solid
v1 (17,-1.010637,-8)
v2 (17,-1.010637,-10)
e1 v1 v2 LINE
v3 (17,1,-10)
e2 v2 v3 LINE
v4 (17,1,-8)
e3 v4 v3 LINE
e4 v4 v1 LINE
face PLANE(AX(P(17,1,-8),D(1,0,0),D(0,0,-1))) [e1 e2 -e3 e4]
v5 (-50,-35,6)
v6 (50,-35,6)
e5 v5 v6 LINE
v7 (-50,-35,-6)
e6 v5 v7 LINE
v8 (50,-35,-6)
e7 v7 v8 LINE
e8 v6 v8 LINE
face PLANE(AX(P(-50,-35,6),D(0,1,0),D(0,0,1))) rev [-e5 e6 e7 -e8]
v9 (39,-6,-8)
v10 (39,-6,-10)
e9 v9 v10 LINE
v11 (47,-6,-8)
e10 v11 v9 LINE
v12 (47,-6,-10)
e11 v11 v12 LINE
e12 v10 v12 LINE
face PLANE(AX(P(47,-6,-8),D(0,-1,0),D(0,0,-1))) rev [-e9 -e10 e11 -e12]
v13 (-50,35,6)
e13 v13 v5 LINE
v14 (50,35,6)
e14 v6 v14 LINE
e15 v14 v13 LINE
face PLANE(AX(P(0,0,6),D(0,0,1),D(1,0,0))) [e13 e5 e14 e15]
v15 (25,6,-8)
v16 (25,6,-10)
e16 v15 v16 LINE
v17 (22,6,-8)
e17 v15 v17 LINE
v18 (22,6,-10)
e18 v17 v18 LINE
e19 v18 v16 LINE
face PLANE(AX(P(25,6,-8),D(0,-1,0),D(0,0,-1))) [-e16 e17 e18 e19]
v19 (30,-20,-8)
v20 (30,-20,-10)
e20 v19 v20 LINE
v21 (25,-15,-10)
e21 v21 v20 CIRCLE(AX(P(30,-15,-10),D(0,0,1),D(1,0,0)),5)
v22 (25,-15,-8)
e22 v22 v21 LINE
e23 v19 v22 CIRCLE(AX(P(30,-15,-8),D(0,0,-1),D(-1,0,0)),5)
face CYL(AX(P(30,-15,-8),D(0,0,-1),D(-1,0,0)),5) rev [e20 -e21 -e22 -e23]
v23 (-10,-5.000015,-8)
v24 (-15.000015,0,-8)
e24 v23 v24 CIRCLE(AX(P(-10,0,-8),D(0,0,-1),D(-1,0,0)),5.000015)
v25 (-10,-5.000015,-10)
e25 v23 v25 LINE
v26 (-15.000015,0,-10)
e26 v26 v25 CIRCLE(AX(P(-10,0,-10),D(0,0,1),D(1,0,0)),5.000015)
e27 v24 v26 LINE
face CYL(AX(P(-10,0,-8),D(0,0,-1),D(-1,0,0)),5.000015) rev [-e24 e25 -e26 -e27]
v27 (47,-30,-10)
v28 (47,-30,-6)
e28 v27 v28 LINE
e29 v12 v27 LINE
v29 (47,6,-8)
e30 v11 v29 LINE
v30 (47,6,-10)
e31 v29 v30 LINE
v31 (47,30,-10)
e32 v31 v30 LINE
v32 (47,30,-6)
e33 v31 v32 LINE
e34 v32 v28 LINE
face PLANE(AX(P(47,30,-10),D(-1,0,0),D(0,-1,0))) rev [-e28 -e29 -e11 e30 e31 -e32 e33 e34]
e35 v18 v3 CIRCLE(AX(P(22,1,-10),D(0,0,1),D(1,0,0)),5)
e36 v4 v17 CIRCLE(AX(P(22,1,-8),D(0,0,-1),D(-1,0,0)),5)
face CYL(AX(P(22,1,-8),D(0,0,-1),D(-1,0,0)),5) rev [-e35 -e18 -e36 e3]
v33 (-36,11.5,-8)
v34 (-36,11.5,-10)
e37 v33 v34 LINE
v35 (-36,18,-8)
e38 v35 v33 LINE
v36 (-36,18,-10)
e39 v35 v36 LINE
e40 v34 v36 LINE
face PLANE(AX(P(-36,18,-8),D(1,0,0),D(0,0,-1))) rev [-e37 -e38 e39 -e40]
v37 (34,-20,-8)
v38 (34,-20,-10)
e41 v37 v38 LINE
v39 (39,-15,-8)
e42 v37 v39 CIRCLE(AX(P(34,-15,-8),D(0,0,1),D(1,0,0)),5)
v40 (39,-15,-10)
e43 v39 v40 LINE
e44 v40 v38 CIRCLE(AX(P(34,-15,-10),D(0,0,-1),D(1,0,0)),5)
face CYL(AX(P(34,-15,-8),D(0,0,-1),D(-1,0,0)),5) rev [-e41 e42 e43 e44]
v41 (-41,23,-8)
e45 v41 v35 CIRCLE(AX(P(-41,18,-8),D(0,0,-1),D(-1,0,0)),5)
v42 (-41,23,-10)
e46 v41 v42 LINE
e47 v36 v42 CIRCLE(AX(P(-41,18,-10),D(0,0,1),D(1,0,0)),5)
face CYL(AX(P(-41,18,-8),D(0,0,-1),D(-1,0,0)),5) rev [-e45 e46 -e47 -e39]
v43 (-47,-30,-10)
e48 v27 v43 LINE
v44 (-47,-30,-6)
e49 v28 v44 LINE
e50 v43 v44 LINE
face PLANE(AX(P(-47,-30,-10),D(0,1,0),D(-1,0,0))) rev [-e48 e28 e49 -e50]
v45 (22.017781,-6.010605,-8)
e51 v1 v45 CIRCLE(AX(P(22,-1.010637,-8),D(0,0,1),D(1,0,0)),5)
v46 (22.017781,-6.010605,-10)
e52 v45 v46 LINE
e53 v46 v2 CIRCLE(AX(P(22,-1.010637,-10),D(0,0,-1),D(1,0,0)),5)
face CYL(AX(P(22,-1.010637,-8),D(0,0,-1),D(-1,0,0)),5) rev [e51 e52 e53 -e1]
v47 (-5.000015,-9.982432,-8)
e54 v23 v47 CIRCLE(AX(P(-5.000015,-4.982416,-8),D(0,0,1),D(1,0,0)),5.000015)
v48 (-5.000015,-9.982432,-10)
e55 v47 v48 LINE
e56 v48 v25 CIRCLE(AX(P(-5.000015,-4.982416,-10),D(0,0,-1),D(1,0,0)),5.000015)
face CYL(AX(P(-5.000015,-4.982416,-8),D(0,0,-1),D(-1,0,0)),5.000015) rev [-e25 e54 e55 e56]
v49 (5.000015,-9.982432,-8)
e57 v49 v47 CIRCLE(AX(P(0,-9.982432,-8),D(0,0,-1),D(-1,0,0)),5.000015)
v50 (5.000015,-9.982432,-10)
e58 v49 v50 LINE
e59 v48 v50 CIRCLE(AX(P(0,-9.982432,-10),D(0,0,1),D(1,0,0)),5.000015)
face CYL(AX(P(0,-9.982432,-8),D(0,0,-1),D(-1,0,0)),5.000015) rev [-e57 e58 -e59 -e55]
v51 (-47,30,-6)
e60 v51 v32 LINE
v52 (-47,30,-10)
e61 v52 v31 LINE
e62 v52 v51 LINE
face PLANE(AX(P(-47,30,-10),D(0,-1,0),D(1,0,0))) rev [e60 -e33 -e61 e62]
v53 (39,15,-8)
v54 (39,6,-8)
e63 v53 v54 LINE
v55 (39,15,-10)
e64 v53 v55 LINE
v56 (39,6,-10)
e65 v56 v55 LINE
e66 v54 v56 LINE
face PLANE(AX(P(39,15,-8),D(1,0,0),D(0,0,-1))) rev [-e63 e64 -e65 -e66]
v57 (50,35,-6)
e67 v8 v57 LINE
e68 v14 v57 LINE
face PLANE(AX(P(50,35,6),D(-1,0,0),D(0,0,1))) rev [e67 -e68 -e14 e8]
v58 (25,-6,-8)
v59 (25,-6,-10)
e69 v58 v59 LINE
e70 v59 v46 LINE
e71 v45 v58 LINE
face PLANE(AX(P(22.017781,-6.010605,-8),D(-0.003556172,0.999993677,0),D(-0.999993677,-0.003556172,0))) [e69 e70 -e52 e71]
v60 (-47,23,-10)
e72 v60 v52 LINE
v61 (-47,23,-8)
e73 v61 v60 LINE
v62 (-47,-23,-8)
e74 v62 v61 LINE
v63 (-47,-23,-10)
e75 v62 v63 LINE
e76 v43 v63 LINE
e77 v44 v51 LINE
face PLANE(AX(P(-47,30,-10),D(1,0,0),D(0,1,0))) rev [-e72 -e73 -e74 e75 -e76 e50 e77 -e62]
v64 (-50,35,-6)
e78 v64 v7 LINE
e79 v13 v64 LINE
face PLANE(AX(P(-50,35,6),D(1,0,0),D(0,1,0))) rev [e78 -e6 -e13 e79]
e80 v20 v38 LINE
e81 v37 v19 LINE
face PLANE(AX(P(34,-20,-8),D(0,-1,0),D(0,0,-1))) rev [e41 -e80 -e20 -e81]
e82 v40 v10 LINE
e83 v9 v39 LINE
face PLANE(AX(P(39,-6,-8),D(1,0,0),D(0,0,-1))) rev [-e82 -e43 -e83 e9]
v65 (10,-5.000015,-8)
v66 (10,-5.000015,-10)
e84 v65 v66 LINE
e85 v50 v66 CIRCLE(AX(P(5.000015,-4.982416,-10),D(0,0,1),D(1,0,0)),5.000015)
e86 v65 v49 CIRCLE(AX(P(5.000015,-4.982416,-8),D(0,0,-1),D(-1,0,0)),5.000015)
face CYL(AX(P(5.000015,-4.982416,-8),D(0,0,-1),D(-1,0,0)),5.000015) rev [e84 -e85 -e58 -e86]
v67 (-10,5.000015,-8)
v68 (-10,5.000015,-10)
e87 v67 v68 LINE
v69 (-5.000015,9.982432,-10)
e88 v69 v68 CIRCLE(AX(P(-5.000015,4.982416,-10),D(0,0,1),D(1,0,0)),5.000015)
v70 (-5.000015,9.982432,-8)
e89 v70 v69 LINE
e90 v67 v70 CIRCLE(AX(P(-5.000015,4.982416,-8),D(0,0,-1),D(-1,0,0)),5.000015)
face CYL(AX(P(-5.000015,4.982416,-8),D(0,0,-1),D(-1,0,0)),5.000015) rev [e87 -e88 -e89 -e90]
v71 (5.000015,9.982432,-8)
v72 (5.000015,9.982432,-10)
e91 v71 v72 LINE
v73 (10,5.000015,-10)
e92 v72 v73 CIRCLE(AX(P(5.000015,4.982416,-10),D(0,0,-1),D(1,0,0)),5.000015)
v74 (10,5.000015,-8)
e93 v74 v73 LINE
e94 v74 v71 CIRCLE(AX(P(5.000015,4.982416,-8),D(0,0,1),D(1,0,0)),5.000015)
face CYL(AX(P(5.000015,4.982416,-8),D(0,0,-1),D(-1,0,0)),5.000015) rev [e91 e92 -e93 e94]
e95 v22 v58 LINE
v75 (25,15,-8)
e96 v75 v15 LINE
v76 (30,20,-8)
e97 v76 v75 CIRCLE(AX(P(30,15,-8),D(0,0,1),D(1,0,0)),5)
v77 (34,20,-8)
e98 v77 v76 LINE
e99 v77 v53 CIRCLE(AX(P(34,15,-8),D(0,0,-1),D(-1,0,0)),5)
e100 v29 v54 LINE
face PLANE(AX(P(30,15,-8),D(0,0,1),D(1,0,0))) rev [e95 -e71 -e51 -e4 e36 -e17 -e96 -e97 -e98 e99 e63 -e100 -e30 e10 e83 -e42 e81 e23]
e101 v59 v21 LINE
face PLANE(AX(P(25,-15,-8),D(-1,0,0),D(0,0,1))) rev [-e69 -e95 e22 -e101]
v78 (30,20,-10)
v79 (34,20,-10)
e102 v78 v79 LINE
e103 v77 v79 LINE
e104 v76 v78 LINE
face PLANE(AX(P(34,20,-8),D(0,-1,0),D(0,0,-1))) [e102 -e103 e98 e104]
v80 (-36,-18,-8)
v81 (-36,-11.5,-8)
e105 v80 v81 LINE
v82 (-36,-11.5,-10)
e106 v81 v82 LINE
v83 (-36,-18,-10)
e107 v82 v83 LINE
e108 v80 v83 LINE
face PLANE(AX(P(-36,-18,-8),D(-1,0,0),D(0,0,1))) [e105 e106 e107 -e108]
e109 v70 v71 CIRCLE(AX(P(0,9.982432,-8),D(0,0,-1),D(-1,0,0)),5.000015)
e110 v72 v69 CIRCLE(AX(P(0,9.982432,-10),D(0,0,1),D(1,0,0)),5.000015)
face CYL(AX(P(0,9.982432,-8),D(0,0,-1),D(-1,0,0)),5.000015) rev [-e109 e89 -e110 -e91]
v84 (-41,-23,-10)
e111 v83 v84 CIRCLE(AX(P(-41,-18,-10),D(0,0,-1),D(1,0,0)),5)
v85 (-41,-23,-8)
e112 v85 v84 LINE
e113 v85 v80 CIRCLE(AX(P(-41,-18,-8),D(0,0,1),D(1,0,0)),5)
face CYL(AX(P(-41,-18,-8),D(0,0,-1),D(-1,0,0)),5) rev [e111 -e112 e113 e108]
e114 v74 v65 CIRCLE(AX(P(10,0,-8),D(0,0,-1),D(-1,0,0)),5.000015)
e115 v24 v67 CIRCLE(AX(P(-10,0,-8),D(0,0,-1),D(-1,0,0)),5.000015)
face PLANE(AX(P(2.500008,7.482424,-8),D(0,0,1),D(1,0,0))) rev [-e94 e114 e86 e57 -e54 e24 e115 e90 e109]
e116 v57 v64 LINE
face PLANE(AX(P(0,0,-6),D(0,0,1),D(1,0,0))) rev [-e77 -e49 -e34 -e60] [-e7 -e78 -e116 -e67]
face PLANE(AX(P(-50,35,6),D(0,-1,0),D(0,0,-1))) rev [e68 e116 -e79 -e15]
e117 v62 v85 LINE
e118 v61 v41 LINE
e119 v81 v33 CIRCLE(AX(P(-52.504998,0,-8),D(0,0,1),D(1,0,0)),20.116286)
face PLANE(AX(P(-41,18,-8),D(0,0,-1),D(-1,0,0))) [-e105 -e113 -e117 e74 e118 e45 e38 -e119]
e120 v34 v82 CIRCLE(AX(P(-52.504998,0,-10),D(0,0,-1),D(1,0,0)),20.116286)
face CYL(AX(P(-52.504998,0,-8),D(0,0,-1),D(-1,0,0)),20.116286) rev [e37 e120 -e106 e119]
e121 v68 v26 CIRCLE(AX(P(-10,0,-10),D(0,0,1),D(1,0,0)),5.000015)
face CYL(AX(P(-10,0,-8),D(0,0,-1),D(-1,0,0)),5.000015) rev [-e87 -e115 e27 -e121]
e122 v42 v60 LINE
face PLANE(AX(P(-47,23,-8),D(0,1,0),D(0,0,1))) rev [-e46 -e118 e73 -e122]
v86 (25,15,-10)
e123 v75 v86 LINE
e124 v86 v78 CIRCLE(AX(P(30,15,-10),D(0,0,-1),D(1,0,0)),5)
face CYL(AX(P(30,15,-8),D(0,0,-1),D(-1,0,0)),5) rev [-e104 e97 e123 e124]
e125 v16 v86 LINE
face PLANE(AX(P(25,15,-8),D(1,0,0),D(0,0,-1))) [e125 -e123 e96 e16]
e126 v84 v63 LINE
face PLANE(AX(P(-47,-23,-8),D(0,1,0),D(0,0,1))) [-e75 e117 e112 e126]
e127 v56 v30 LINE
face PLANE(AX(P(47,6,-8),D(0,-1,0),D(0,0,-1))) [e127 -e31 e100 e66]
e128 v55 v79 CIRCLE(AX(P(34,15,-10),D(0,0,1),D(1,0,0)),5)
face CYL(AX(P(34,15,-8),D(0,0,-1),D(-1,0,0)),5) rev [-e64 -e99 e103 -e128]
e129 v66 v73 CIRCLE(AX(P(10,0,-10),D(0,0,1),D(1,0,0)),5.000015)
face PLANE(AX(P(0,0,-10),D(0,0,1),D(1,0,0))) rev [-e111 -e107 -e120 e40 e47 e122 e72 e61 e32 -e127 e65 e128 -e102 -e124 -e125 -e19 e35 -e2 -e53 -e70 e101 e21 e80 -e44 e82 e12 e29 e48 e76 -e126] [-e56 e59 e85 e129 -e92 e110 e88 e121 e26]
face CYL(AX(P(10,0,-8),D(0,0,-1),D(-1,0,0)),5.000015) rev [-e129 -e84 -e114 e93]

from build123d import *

# Parameters (mm, degrees)
BASE_PLATE_SKETCH_W        = 100
BASE_PLATE_SKETCH_H        = 70
BASE_PLATE_100X70X12_DEPTH = 6
RAISED_PAD_SKETCH_W        = 94
RAISED_PAD_SKETCH_H        = 60
RAISED_PAD_94X60X4_DEPTH   = 4
PAD_CUT_1_DEPTH            = 2
PAD_CUT_2_DEPTH            = 2
PAD_CUT_3_DEPTH            = 2


with BuildPart() as part:
    # Base Plate Sketch → Base Plate 100x70x12 (new, symmetric)
    with BuildSketch(Plane.XY):
        Rectangle(BASE_PLATE_SKETCH_W, BASE_PLATE_SKETCH_H)
    extrude(amount=BASE_PLATE_100X70X12_DEPTH, both=True)

    # Raised Pad Sketch → Raised Pad 94x60x4 (add)
    with BuildSketch(Plane(origin=(0, 0, -6), x_dir=(-1, 0, 0), z_dir=(0, 0, -1))):
        Rectangle(RAISED_PAD_SKETCH_W, RAISED_PAD_SKETCH_H)
    extrude(amount=RAISED_PAD_94X60X4_DEPTH)

    # Pad Cut 1 Sketch → Pad Cut 1 (cut, symmetric)
    with BuildSketch(Plane(origin=(0, 0, -10), x_dir=(-1, 0, 0), z_dir=(0, 0, -1))):
        with BuildLine():
            Line((47, -23), (47, 23))
            Line((47, 23), (41, 23))
            ThreePointArc((41, 23), (37.464466094, 21.535533906), (36, 18))
            Line((36, 18), (36, 11.5))
            ThreePointArc((36, 11.5), (32.388712156, 0), (36, -11.5))
            Line((36, -11.5), (36, -18))
            ThreePointArc((36, -18), (37.464466094, -21.535533906), (41, -23))
            Line((41, -23), (47, -23))
        make_face()
    extrude(amount=PAD_CUT_1_DEPTH, both=True, mode=Mode.SUBTRACT)

    # Pad Cut 2 Sketch → Pad Cut 2 (cut, symmetric)
    with BuildSketch(Plane(origin=(0, 0, -10), x_dir=(-1, 0, 0), z_dir=(0, 0, -1))):
        with BuildLine():
            Line((-47, -6), (-39, -6))
            Line((-39, -6), (-39, -15))
            ThreePointArc((-39, -15), (-37.535533906, -18.535533906), (-34, -20))
            Line((-34, -20), (-30, -20))
            ThreePointArc((-30, -20), (-26.464466094, -18.535533906), (-25, -15))
            Line((-25, -15), (-25, -6))
            Line((-25, -6), (-22.017780858, -6.01060535))
            ThreePointArc((-22.017780858, -6.01060535), (-18.470758176, -4.552451776), (-17, -1.010636966))
            Line((-17, -1.010636966), (-17, 1))
            ThreePointArc((-17, 1), (-18.464466094, 4.535533906), (-22, 6))
            Line((-22, 6), (-25, 6))
            Line((-25, 6), (-25, 15))
            ThreePointArc((-25, 15), (-26.464466094, 18.535533906), (-30, 20))
            Line((-30, 20), (-34, 20))
            ThreePointArc((-34, 20), (-37.535533906, 18.535533906), (-39, 15))
            Line((-39, 15), (-39, 6))
            Line((-39, 6), (-47, 6))
            Line((-47, 6), (-47, -6))
        make_face()
    extrude(amount=PAD_CUT_2_DEPTH, both=True, mode=Mode.SUBTRACT)

    # Pad Cut 3 Sketch → Pad Cut 3 (cut, symmetric)
    with BuildSketch(Plane(origin=(0, 0, -10), x_dir=(-1, 0, 0), z_dir=(0, 0, -1))):
        with BuildLine():
            ThreePointArc((-10, 5.000015487), (-15.000015487, 0), (-10, -5.000015487))
            ThreePointArc((-10, -5.000015487), (-8.529332614, -8.524177957), (-5.000015487, -9.982431809))
            ThreePointArc((-5.000015487, -9.982431809), (0, -14.982447295), (5.000015487, -9.982431809))
            ThreePointArc((5.000015487, -9.982431809), (8.529332614, -8.524177957), (10, -5.000015487))
            ThreePointArc((10, -5.000015487), (15.000015487, 0), (10, 5.000015487))
            ThreePointArc((10, 5.000015487), (8.529332614, 8.524177957), (5.000015487, 9.982431809))
            ThreePointArc((5.000015487, 9.982431809), (0, 14.982447295), (-5.000015487, 9.982431809))
            ThreePointArc((-5.000015487, 9.982431809), (-8.529332614, 8.524177957), (-10, 5.000015487))
        make_face()
    extrude(amount=PAD_CUT_3_DEPTH, both=True, mode=Mode.SUBTRACT)


solid = part.part
